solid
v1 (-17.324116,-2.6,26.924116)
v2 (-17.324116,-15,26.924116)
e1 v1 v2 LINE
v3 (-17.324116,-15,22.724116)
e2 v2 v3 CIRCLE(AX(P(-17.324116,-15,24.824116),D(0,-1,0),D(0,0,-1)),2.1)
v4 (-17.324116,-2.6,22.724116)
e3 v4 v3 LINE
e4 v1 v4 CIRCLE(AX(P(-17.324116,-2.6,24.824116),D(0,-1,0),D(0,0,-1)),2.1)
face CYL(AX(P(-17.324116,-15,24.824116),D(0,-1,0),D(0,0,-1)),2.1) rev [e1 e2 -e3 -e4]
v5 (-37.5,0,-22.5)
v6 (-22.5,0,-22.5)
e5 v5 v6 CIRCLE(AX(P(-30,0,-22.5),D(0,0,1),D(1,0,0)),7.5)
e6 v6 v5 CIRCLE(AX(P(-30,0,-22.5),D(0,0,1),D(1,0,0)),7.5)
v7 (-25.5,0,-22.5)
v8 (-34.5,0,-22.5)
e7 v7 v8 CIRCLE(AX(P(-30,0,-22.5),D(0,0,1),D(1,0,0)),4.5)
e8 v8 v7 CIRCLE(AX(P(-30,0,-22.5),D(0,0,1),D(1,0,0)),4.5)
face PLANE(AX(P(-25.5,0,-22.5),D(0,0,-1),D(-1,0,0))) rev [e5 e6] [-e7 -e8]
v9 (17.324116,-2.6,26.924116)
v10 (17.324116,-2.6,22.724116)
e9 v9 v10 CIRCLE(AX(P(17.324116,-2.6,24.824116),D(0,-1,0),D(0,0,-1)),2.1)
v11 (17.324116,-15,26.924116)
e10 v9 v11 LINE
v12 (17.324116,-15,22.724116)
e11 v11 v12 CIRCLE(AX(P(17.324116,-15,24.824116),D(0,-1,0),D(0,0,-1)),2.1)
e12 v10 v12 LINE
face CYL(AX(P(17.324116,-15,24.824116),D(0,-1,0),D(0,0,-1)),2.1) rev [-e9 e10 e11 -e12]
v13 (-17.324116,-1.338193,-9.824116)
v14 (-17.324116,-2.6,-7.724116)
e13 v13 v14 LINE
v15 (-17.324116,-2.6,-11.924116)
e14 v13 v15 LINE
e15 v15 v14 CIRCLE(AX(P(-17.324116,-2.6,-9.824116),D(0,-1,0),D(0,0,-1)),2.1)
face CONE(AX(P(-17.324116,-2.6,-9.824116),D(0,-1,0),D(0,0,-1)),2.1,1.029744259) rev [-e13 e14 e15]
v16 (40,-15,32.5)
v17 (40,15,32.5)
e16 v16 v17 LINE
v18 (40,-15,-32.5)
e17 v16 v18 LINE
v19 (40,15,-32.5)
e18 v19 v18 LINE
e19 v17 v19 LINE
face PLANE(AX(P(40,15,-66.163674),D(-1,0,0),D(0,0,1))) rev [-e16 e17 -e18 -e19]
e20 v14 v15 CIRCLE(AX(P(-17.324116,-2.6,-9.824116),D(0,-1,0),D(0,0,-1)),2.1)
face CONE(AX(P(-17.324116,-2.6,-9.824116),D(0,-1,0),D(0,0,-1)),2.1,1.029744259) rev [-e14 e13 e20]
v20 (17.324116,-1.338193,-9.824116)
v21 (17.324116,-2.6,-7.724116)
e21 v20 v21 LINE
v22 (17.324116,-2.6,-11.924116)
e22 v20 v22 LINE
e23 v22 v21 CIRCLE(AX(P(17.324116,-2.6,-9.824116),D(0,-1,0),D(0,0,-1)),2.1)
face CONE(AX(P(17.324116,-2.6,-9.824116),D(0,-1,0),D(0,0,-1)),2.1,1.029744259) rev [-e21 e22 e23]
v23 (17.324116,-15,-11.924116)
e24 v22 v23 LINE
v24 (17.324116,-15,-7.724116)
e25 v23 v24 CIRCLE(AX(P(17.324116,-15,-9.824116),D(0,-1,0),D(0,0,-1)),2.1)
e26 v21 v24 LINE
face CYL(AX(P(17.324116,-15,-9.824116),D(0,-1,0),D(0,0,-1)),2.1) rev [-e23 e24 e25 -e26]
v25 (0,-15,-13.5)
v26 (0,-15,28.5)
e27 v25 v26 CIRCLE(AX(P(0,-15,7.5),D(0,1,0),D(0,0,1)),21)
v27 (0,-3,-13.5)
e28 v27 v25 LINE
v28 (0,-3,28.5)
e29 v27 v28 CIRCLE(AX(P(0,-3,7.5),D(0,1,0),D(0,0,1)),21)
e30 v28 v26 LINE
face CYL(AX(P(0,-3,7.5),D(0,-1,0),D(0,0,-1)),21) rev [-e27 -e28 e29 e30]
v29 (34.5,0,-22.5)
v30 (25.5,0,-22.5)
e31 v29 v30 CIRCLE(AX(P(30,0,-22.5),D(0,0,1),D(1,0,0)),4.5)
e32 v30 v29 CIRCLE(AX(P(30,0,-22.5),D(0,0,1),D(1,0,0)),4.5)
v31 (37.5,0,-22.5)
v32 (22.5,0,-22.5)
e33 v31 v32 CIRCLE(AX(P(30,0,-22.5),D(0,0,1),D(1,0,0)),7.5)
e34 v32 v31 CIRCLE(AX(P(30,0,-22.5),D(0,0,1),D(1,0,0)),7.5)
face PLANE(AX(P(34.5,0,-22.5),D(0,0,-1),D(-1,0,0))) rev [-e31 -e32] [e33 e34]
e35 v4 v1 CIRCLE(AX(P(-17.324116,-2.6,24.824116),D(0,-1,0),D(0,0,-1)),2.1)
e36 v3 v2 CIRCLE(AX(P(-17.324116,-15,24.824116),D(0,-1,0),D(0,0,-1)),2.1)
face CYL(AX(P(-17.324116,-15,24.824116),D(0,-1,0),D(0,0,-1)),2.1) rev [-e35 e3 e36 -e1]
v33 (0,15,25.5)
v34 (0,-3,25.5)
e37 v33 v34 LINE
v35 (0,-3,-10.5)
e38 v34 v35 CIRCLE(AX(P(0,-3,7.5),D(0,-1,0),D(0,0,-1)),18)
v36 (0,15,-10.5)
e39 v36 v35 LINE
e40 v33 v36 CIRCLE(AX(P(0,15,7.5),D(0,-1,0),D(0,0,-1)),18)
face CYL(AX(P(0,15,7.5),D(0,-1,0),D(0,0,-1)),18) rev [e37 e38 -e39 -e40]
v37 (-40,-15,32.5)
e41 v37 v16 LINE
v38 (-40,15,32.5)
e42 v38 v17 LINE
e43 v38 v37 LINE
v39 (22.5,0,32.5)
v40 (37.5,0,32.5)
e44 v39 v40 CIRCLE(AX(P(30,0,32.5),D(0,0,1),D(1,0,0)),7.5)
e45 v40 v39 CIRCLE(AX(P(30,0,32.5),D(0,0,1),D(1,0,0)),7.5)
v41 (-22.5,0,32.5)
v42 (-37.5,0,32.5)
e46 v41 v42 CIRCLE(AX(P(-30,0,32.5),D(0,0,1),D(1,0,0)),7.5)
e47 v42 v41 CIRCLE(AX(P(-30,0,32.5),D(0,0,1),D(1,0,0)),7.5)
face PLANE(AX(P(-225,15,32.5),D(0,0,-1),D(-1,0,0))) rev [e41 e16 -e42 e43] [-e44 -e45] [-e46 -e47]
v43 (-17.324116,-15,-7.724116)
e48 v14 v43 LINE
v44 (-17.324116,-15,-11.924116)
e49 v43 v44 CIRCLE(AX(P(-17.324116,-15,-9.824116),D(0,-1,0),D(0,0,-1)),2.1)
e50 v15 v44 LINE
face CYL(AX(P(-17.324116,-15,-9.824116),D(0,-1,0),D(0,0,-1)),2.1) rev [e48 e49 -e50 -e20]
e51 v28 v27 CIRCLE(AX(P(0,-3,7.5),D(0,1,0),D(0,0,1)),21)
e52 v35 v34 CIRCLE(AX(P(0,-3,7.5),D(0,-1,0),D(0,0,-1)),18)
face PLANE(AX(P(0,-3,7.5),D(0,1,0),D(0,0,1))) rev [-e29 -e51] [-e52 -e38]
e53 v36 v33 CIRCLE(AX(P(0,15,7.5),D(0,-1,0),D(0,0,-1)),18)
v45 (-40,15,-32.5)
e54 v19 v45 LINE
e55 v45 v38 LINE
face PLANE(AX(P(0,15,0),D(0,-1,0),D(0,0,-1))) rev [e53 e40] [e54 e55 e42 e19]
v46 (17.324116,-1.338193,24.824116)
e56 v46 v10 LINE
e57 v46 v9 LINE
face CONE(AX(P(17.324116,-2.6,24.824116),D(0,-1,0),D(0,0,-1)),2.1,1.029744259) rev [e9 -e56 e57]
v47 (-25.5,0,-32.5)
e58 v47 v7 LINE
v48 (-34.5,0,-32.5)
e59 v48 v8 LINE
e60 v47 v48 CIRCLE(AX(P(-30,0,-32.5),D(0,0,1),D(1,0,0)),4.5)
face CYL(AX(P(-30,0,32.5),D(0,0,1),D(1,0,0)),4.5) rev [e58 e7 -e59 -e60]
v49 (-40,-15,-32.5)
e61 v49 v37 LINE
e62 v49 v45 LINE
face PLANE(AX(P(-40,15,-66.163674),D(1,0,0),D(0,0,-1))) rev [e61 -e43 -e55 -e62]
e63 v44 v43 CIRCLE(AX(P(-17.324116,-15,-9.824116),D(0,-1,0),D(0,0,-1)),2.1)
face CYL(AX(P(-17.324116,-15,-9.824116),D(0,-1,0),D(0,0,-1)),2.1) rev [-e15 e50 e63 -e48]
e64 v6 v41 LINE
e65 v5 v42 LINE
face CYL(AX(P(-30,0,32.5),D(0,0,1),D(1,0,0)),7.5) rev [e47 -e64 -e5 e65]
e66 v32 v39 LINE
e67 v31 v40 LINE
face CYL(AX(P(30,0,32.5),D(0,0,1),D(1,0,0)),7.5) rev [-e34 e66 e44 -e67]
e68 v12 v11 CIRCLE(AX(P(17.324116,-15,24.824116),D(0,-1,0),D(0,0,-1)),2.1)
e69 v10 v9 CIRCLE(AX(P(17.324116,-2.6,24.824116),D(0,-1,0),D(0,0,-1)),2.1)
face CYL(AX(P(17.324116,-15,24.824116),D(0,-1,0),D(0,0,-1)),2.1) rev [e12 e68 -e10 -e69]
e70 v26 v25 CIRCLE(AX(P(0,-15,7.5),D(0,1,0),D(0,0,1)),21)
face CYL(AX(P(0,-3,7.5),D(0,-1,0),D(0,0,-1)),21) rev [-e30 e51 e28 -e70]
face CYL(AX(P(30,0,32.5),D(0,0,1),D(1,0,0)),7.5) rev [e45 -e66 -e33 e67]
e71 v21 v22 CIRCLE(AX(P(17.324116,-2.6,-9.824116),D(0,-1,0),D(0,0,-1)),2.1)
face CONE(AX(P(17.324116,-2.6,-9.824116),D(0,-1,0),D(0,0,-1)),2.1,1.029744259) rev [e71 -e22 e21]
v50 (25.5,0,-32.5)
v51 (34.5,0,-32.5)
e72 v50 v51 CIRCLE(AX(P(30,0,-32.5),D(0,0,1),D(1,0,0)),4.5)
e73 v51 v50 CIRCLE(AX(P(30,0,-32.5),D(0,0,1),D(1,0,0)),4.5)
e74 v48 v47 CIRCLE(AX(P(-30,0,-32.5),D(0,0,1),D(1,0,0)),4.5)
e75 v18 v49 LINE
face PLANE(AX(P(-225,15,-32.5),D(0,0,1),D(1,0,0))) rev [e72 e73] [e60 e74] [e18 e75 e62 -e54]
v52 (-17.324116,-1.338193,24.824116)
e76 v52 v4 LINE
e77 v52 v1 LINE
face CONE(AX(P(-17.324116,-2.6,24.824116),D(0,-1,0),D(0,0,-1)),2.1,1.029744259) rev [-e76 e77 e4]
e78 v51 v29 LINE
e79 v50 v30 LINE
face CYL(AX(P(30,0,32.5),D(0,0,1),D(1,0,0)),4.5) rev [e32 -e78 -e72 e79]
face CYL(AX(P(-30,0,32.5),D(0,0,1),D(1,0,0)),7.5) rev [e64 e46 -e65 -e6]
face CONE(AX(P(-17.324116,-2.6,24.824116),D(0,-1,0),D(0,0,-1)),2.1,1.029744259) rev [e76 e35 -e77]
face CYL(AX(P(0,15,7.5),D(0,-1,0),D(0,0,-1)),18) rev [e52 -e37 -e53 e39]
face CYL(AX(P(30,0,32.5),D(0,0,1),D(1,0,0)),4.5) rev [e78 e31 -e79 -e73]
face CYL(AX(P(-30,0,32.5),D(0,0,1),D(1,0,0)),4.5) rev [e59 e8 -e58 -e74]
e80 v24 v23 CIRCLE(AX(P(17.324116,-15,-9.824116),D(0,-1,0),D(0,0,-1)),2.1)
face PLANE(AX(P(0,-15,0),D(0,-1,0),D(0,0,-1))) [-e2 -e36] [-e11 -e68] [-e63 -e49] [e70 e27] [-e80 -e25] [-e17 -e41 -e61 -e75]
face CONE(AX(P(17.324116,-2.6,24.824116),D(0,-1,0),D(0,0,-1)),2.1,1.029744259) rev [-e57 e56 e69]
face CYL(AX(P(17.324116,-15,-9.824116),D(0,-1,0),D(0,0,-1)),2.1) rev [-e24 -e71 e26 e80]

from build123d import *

# Parameters (mm, degrees)
SKETCH_1_W                  = 450
SKETCH_1_H                  = 65
EXTRUDE_1_DEPTH             = 15
CHAMFER_1_SIZE              = 2
SKETCH_2_R                  = 10
CUT_EXTRUDE_1_DEPTH         = 30
CUT_EXTRUDE_2_DEPTH         = 30
SKETCH_4_R                  = 21
CUT_EXTRUDE_3_DEPTH         = 12
SKETCH_5_R                  = 18
CUT_EXTRUDE_4_DEPTH         = 229.046596116
HOLE_WIZARD_2_D             = 6.6
HOLE_WIZARD_2_DEPTH         = 31.5
HOLE_WIZARD_2_CBORE_D       = 11
HOLE_WIZARD_2_CBORE_DEPTH   = 6.8
HOLE_WIZARD_M6_1_D          = 5
HOLE_WIZARD_2_2_D           = 9
HOLE_WIZARD_2_2_CBORE_D     = 15
HOLE_WIZARD_2_2_CBORE_DEPTH = 55
HOLE_WIZARD_M5_1_D          = 4.2
HOLE_WIZARD_M5_1_DEPTH      = 12.4
HOLE_WIZARD_M5_1_TIP        = 1.2618073
SKETCH_15_W                 = 237.437546179
SKETCH_15_H                 = 159.818796437
CUT_EXTRUDE_6_DEPTH         = 230.306018238


with BuildPart() as part:
    # 草图1 → 凸台-拉伸1 (new, symmetric)
    with BuildSketch(Plane(origin=(0, 0, 0), x_dir=(1, 0, 0), z_dir=(0, 1, 0))):
        Rectangle(SKETCH_1_W, SKETCH_1_H)
    extrude(amount=EXTRUDE_1_DEPTH, both=True)

    # 倒角1
    chamfer_1_edges = [part.edges().sort_by_distance(p)[0] for p in [
        (225, 0, 32.5),
        (-225, 0, 32.5),
    ]]
    chamfer(chamfer_1_edges, length=CHAMFER_1_SIZE)

    # 草图2 → 切除-拉伸1 (cut)
    with BuildSketch(Plane(origin=(0, 15, 0), x_dir=(1, 0, 0), z_dir=(0, 1, 0))):
        with Locations(Location((-200, 0, 0), (0, 0, 270))):
            Circle(SKETCH_2_R)
        with Locations(Location((200, 0, 0), (0, 0, 90))):
            Circle(SKETCH_2_R)
    extrude(amount=-CUT_EXTRUDE_1_DEPTH, mode=Mode.SUBTRACT)

    # 草图3 → 切除-拉伸2 (cut)
    with BuildSketch(Plane(origin=(0, 15, 0), x_dir=(1, 0, 0), z_dir=(0, 1, 0))):
        with BuildLine():
            Line((-225, 1), (-182, 1))
            ThreePointArc((-182, 1), (-181, 0), (-182, -1))
            Line((-182, -1), (-225, -1))
            ThreePointArc((-225, -1), (-226, 0), (-225, 1))
        make_face()
        with BuildLine():
            Line((225, 1), (182, 1))
            ThreePointArc((182, 1), (181, 0), (182, -1))
            Line((182, -1), (225, -1))
            ThreePointArc((225, -1), (226, 0), (225, 1))
        make_face()
    extrude(amount=-CUT_EXTRUDE_2_DEPTH, mode=Mode.SUBTRACT)

    # 草图4 → 切除-拉伸3 (cut)
    with BuildSketch(Plane(origin=(0, -15, 0), x_dir=(1, 0, 0), z_dir=(0, 1, 0))):
        with Locations(Location((0, -7.5, 0), (0, 0, 270))):
            Circle(SKETCH_4_R)
    extrude(amount=CUT_EXTRUDE_3_DEPTH, mode=Mode.SUBTRACT)

    # 草图5 → 切除-拉伸4 (cut, through all)
    with BuildSketch(Plane(origin=(0, -3, 0), x_dir=(-1, 0, 0), z_dir=(0, -1, 0))):
        with Locations(Location((0, -7.5, 0), (0, 0, 90))):
            Circle(SKETCH_5_R)
    extrude(amount=-CUT_EXTRUDE_4_DEPTH, mode=Mode.SUBTRACT)

    # Hole Wizard 2
    with Locations(Plane.XY.offset(32.5)):
        with Locations((215, -7.5), (215, 7.5), (-215, 7.5), (-215, -7.5)):
            CounterBoreHole(HOLE_WIZARD_2_D / 2, HOLE_WIZARD_2_CBORE_D / 2, HOLE_WIZARD_2_CBORE_DEPTH, depth=HOLE_WIZARD_2_DEPTH)

    # M6 螺纹孔1 (through all)
    with Locations(Plane.XY.offset(-1)):
        with Locations((215, -7.5), (215, 7.5), (-215, -7.5), (-215, 7.5)):
            Hole(HOLE_WIZARD_M6_1_D / 2)

    # Hole Wizard 2 2 (through all)
    with Locations(Plane.XY.offset(32.5)):
        with Locations((150, 0), (30, 0), (-30, 0), (-150, 0)):
            CounterBoreHole(HOLE_WIZARD_2_2_D / 2, HOLE_WIZARD_2_2_CBORE_D / 2, HOLE_WIZARD_2_2_CBORE_DEPTH)

    # M5 螺纹孔1
    with Locations(Plane(origin=(0, -15, 0), x_dir=(-1, 0, 0), z_dir=(0, -1, 0))):
        with Locations((-17.324116139, 9.824116139), (17.324116139, 9.824116139), (17.324116139, -24.824116139), (-17.324116139, -24.824116139)):
            Hole(HOLE_WIZARD_M5_1_D / 2, depth=HOLE_WIZARD_M5_1_DEPTH)
            with Locations((0, 0, -(HOLE_WIZARD_M5_1_DEPTH + HOLE_WIZARD_M5_1_TIP / 2))):  # 118° drill point
                Cone(0, HOLE_WIZARD_M5_1_D / 2, HOLE_WIZARD_M5_1_TIP, mode=Mode.SUBTRACT)

    # 草图15 → 切除-拉伸6 (cut, through all)
    with BuildSketch(Plane.XZ.offset(15)):
        with Locations((158.71877309, 13.745723836)):
            Rectangle(SKETCH_15_W, SKETCH_15_H)
        with Locations((-158.71877309, 13.745723836)):
            Rectangle(SKETCH_15_W, SKETCH_15_H)
    extrude(amount=-CUT_EXTRUDE_6_DEPTH, mode=Mode.SUBTRACT)


solid = part.part
